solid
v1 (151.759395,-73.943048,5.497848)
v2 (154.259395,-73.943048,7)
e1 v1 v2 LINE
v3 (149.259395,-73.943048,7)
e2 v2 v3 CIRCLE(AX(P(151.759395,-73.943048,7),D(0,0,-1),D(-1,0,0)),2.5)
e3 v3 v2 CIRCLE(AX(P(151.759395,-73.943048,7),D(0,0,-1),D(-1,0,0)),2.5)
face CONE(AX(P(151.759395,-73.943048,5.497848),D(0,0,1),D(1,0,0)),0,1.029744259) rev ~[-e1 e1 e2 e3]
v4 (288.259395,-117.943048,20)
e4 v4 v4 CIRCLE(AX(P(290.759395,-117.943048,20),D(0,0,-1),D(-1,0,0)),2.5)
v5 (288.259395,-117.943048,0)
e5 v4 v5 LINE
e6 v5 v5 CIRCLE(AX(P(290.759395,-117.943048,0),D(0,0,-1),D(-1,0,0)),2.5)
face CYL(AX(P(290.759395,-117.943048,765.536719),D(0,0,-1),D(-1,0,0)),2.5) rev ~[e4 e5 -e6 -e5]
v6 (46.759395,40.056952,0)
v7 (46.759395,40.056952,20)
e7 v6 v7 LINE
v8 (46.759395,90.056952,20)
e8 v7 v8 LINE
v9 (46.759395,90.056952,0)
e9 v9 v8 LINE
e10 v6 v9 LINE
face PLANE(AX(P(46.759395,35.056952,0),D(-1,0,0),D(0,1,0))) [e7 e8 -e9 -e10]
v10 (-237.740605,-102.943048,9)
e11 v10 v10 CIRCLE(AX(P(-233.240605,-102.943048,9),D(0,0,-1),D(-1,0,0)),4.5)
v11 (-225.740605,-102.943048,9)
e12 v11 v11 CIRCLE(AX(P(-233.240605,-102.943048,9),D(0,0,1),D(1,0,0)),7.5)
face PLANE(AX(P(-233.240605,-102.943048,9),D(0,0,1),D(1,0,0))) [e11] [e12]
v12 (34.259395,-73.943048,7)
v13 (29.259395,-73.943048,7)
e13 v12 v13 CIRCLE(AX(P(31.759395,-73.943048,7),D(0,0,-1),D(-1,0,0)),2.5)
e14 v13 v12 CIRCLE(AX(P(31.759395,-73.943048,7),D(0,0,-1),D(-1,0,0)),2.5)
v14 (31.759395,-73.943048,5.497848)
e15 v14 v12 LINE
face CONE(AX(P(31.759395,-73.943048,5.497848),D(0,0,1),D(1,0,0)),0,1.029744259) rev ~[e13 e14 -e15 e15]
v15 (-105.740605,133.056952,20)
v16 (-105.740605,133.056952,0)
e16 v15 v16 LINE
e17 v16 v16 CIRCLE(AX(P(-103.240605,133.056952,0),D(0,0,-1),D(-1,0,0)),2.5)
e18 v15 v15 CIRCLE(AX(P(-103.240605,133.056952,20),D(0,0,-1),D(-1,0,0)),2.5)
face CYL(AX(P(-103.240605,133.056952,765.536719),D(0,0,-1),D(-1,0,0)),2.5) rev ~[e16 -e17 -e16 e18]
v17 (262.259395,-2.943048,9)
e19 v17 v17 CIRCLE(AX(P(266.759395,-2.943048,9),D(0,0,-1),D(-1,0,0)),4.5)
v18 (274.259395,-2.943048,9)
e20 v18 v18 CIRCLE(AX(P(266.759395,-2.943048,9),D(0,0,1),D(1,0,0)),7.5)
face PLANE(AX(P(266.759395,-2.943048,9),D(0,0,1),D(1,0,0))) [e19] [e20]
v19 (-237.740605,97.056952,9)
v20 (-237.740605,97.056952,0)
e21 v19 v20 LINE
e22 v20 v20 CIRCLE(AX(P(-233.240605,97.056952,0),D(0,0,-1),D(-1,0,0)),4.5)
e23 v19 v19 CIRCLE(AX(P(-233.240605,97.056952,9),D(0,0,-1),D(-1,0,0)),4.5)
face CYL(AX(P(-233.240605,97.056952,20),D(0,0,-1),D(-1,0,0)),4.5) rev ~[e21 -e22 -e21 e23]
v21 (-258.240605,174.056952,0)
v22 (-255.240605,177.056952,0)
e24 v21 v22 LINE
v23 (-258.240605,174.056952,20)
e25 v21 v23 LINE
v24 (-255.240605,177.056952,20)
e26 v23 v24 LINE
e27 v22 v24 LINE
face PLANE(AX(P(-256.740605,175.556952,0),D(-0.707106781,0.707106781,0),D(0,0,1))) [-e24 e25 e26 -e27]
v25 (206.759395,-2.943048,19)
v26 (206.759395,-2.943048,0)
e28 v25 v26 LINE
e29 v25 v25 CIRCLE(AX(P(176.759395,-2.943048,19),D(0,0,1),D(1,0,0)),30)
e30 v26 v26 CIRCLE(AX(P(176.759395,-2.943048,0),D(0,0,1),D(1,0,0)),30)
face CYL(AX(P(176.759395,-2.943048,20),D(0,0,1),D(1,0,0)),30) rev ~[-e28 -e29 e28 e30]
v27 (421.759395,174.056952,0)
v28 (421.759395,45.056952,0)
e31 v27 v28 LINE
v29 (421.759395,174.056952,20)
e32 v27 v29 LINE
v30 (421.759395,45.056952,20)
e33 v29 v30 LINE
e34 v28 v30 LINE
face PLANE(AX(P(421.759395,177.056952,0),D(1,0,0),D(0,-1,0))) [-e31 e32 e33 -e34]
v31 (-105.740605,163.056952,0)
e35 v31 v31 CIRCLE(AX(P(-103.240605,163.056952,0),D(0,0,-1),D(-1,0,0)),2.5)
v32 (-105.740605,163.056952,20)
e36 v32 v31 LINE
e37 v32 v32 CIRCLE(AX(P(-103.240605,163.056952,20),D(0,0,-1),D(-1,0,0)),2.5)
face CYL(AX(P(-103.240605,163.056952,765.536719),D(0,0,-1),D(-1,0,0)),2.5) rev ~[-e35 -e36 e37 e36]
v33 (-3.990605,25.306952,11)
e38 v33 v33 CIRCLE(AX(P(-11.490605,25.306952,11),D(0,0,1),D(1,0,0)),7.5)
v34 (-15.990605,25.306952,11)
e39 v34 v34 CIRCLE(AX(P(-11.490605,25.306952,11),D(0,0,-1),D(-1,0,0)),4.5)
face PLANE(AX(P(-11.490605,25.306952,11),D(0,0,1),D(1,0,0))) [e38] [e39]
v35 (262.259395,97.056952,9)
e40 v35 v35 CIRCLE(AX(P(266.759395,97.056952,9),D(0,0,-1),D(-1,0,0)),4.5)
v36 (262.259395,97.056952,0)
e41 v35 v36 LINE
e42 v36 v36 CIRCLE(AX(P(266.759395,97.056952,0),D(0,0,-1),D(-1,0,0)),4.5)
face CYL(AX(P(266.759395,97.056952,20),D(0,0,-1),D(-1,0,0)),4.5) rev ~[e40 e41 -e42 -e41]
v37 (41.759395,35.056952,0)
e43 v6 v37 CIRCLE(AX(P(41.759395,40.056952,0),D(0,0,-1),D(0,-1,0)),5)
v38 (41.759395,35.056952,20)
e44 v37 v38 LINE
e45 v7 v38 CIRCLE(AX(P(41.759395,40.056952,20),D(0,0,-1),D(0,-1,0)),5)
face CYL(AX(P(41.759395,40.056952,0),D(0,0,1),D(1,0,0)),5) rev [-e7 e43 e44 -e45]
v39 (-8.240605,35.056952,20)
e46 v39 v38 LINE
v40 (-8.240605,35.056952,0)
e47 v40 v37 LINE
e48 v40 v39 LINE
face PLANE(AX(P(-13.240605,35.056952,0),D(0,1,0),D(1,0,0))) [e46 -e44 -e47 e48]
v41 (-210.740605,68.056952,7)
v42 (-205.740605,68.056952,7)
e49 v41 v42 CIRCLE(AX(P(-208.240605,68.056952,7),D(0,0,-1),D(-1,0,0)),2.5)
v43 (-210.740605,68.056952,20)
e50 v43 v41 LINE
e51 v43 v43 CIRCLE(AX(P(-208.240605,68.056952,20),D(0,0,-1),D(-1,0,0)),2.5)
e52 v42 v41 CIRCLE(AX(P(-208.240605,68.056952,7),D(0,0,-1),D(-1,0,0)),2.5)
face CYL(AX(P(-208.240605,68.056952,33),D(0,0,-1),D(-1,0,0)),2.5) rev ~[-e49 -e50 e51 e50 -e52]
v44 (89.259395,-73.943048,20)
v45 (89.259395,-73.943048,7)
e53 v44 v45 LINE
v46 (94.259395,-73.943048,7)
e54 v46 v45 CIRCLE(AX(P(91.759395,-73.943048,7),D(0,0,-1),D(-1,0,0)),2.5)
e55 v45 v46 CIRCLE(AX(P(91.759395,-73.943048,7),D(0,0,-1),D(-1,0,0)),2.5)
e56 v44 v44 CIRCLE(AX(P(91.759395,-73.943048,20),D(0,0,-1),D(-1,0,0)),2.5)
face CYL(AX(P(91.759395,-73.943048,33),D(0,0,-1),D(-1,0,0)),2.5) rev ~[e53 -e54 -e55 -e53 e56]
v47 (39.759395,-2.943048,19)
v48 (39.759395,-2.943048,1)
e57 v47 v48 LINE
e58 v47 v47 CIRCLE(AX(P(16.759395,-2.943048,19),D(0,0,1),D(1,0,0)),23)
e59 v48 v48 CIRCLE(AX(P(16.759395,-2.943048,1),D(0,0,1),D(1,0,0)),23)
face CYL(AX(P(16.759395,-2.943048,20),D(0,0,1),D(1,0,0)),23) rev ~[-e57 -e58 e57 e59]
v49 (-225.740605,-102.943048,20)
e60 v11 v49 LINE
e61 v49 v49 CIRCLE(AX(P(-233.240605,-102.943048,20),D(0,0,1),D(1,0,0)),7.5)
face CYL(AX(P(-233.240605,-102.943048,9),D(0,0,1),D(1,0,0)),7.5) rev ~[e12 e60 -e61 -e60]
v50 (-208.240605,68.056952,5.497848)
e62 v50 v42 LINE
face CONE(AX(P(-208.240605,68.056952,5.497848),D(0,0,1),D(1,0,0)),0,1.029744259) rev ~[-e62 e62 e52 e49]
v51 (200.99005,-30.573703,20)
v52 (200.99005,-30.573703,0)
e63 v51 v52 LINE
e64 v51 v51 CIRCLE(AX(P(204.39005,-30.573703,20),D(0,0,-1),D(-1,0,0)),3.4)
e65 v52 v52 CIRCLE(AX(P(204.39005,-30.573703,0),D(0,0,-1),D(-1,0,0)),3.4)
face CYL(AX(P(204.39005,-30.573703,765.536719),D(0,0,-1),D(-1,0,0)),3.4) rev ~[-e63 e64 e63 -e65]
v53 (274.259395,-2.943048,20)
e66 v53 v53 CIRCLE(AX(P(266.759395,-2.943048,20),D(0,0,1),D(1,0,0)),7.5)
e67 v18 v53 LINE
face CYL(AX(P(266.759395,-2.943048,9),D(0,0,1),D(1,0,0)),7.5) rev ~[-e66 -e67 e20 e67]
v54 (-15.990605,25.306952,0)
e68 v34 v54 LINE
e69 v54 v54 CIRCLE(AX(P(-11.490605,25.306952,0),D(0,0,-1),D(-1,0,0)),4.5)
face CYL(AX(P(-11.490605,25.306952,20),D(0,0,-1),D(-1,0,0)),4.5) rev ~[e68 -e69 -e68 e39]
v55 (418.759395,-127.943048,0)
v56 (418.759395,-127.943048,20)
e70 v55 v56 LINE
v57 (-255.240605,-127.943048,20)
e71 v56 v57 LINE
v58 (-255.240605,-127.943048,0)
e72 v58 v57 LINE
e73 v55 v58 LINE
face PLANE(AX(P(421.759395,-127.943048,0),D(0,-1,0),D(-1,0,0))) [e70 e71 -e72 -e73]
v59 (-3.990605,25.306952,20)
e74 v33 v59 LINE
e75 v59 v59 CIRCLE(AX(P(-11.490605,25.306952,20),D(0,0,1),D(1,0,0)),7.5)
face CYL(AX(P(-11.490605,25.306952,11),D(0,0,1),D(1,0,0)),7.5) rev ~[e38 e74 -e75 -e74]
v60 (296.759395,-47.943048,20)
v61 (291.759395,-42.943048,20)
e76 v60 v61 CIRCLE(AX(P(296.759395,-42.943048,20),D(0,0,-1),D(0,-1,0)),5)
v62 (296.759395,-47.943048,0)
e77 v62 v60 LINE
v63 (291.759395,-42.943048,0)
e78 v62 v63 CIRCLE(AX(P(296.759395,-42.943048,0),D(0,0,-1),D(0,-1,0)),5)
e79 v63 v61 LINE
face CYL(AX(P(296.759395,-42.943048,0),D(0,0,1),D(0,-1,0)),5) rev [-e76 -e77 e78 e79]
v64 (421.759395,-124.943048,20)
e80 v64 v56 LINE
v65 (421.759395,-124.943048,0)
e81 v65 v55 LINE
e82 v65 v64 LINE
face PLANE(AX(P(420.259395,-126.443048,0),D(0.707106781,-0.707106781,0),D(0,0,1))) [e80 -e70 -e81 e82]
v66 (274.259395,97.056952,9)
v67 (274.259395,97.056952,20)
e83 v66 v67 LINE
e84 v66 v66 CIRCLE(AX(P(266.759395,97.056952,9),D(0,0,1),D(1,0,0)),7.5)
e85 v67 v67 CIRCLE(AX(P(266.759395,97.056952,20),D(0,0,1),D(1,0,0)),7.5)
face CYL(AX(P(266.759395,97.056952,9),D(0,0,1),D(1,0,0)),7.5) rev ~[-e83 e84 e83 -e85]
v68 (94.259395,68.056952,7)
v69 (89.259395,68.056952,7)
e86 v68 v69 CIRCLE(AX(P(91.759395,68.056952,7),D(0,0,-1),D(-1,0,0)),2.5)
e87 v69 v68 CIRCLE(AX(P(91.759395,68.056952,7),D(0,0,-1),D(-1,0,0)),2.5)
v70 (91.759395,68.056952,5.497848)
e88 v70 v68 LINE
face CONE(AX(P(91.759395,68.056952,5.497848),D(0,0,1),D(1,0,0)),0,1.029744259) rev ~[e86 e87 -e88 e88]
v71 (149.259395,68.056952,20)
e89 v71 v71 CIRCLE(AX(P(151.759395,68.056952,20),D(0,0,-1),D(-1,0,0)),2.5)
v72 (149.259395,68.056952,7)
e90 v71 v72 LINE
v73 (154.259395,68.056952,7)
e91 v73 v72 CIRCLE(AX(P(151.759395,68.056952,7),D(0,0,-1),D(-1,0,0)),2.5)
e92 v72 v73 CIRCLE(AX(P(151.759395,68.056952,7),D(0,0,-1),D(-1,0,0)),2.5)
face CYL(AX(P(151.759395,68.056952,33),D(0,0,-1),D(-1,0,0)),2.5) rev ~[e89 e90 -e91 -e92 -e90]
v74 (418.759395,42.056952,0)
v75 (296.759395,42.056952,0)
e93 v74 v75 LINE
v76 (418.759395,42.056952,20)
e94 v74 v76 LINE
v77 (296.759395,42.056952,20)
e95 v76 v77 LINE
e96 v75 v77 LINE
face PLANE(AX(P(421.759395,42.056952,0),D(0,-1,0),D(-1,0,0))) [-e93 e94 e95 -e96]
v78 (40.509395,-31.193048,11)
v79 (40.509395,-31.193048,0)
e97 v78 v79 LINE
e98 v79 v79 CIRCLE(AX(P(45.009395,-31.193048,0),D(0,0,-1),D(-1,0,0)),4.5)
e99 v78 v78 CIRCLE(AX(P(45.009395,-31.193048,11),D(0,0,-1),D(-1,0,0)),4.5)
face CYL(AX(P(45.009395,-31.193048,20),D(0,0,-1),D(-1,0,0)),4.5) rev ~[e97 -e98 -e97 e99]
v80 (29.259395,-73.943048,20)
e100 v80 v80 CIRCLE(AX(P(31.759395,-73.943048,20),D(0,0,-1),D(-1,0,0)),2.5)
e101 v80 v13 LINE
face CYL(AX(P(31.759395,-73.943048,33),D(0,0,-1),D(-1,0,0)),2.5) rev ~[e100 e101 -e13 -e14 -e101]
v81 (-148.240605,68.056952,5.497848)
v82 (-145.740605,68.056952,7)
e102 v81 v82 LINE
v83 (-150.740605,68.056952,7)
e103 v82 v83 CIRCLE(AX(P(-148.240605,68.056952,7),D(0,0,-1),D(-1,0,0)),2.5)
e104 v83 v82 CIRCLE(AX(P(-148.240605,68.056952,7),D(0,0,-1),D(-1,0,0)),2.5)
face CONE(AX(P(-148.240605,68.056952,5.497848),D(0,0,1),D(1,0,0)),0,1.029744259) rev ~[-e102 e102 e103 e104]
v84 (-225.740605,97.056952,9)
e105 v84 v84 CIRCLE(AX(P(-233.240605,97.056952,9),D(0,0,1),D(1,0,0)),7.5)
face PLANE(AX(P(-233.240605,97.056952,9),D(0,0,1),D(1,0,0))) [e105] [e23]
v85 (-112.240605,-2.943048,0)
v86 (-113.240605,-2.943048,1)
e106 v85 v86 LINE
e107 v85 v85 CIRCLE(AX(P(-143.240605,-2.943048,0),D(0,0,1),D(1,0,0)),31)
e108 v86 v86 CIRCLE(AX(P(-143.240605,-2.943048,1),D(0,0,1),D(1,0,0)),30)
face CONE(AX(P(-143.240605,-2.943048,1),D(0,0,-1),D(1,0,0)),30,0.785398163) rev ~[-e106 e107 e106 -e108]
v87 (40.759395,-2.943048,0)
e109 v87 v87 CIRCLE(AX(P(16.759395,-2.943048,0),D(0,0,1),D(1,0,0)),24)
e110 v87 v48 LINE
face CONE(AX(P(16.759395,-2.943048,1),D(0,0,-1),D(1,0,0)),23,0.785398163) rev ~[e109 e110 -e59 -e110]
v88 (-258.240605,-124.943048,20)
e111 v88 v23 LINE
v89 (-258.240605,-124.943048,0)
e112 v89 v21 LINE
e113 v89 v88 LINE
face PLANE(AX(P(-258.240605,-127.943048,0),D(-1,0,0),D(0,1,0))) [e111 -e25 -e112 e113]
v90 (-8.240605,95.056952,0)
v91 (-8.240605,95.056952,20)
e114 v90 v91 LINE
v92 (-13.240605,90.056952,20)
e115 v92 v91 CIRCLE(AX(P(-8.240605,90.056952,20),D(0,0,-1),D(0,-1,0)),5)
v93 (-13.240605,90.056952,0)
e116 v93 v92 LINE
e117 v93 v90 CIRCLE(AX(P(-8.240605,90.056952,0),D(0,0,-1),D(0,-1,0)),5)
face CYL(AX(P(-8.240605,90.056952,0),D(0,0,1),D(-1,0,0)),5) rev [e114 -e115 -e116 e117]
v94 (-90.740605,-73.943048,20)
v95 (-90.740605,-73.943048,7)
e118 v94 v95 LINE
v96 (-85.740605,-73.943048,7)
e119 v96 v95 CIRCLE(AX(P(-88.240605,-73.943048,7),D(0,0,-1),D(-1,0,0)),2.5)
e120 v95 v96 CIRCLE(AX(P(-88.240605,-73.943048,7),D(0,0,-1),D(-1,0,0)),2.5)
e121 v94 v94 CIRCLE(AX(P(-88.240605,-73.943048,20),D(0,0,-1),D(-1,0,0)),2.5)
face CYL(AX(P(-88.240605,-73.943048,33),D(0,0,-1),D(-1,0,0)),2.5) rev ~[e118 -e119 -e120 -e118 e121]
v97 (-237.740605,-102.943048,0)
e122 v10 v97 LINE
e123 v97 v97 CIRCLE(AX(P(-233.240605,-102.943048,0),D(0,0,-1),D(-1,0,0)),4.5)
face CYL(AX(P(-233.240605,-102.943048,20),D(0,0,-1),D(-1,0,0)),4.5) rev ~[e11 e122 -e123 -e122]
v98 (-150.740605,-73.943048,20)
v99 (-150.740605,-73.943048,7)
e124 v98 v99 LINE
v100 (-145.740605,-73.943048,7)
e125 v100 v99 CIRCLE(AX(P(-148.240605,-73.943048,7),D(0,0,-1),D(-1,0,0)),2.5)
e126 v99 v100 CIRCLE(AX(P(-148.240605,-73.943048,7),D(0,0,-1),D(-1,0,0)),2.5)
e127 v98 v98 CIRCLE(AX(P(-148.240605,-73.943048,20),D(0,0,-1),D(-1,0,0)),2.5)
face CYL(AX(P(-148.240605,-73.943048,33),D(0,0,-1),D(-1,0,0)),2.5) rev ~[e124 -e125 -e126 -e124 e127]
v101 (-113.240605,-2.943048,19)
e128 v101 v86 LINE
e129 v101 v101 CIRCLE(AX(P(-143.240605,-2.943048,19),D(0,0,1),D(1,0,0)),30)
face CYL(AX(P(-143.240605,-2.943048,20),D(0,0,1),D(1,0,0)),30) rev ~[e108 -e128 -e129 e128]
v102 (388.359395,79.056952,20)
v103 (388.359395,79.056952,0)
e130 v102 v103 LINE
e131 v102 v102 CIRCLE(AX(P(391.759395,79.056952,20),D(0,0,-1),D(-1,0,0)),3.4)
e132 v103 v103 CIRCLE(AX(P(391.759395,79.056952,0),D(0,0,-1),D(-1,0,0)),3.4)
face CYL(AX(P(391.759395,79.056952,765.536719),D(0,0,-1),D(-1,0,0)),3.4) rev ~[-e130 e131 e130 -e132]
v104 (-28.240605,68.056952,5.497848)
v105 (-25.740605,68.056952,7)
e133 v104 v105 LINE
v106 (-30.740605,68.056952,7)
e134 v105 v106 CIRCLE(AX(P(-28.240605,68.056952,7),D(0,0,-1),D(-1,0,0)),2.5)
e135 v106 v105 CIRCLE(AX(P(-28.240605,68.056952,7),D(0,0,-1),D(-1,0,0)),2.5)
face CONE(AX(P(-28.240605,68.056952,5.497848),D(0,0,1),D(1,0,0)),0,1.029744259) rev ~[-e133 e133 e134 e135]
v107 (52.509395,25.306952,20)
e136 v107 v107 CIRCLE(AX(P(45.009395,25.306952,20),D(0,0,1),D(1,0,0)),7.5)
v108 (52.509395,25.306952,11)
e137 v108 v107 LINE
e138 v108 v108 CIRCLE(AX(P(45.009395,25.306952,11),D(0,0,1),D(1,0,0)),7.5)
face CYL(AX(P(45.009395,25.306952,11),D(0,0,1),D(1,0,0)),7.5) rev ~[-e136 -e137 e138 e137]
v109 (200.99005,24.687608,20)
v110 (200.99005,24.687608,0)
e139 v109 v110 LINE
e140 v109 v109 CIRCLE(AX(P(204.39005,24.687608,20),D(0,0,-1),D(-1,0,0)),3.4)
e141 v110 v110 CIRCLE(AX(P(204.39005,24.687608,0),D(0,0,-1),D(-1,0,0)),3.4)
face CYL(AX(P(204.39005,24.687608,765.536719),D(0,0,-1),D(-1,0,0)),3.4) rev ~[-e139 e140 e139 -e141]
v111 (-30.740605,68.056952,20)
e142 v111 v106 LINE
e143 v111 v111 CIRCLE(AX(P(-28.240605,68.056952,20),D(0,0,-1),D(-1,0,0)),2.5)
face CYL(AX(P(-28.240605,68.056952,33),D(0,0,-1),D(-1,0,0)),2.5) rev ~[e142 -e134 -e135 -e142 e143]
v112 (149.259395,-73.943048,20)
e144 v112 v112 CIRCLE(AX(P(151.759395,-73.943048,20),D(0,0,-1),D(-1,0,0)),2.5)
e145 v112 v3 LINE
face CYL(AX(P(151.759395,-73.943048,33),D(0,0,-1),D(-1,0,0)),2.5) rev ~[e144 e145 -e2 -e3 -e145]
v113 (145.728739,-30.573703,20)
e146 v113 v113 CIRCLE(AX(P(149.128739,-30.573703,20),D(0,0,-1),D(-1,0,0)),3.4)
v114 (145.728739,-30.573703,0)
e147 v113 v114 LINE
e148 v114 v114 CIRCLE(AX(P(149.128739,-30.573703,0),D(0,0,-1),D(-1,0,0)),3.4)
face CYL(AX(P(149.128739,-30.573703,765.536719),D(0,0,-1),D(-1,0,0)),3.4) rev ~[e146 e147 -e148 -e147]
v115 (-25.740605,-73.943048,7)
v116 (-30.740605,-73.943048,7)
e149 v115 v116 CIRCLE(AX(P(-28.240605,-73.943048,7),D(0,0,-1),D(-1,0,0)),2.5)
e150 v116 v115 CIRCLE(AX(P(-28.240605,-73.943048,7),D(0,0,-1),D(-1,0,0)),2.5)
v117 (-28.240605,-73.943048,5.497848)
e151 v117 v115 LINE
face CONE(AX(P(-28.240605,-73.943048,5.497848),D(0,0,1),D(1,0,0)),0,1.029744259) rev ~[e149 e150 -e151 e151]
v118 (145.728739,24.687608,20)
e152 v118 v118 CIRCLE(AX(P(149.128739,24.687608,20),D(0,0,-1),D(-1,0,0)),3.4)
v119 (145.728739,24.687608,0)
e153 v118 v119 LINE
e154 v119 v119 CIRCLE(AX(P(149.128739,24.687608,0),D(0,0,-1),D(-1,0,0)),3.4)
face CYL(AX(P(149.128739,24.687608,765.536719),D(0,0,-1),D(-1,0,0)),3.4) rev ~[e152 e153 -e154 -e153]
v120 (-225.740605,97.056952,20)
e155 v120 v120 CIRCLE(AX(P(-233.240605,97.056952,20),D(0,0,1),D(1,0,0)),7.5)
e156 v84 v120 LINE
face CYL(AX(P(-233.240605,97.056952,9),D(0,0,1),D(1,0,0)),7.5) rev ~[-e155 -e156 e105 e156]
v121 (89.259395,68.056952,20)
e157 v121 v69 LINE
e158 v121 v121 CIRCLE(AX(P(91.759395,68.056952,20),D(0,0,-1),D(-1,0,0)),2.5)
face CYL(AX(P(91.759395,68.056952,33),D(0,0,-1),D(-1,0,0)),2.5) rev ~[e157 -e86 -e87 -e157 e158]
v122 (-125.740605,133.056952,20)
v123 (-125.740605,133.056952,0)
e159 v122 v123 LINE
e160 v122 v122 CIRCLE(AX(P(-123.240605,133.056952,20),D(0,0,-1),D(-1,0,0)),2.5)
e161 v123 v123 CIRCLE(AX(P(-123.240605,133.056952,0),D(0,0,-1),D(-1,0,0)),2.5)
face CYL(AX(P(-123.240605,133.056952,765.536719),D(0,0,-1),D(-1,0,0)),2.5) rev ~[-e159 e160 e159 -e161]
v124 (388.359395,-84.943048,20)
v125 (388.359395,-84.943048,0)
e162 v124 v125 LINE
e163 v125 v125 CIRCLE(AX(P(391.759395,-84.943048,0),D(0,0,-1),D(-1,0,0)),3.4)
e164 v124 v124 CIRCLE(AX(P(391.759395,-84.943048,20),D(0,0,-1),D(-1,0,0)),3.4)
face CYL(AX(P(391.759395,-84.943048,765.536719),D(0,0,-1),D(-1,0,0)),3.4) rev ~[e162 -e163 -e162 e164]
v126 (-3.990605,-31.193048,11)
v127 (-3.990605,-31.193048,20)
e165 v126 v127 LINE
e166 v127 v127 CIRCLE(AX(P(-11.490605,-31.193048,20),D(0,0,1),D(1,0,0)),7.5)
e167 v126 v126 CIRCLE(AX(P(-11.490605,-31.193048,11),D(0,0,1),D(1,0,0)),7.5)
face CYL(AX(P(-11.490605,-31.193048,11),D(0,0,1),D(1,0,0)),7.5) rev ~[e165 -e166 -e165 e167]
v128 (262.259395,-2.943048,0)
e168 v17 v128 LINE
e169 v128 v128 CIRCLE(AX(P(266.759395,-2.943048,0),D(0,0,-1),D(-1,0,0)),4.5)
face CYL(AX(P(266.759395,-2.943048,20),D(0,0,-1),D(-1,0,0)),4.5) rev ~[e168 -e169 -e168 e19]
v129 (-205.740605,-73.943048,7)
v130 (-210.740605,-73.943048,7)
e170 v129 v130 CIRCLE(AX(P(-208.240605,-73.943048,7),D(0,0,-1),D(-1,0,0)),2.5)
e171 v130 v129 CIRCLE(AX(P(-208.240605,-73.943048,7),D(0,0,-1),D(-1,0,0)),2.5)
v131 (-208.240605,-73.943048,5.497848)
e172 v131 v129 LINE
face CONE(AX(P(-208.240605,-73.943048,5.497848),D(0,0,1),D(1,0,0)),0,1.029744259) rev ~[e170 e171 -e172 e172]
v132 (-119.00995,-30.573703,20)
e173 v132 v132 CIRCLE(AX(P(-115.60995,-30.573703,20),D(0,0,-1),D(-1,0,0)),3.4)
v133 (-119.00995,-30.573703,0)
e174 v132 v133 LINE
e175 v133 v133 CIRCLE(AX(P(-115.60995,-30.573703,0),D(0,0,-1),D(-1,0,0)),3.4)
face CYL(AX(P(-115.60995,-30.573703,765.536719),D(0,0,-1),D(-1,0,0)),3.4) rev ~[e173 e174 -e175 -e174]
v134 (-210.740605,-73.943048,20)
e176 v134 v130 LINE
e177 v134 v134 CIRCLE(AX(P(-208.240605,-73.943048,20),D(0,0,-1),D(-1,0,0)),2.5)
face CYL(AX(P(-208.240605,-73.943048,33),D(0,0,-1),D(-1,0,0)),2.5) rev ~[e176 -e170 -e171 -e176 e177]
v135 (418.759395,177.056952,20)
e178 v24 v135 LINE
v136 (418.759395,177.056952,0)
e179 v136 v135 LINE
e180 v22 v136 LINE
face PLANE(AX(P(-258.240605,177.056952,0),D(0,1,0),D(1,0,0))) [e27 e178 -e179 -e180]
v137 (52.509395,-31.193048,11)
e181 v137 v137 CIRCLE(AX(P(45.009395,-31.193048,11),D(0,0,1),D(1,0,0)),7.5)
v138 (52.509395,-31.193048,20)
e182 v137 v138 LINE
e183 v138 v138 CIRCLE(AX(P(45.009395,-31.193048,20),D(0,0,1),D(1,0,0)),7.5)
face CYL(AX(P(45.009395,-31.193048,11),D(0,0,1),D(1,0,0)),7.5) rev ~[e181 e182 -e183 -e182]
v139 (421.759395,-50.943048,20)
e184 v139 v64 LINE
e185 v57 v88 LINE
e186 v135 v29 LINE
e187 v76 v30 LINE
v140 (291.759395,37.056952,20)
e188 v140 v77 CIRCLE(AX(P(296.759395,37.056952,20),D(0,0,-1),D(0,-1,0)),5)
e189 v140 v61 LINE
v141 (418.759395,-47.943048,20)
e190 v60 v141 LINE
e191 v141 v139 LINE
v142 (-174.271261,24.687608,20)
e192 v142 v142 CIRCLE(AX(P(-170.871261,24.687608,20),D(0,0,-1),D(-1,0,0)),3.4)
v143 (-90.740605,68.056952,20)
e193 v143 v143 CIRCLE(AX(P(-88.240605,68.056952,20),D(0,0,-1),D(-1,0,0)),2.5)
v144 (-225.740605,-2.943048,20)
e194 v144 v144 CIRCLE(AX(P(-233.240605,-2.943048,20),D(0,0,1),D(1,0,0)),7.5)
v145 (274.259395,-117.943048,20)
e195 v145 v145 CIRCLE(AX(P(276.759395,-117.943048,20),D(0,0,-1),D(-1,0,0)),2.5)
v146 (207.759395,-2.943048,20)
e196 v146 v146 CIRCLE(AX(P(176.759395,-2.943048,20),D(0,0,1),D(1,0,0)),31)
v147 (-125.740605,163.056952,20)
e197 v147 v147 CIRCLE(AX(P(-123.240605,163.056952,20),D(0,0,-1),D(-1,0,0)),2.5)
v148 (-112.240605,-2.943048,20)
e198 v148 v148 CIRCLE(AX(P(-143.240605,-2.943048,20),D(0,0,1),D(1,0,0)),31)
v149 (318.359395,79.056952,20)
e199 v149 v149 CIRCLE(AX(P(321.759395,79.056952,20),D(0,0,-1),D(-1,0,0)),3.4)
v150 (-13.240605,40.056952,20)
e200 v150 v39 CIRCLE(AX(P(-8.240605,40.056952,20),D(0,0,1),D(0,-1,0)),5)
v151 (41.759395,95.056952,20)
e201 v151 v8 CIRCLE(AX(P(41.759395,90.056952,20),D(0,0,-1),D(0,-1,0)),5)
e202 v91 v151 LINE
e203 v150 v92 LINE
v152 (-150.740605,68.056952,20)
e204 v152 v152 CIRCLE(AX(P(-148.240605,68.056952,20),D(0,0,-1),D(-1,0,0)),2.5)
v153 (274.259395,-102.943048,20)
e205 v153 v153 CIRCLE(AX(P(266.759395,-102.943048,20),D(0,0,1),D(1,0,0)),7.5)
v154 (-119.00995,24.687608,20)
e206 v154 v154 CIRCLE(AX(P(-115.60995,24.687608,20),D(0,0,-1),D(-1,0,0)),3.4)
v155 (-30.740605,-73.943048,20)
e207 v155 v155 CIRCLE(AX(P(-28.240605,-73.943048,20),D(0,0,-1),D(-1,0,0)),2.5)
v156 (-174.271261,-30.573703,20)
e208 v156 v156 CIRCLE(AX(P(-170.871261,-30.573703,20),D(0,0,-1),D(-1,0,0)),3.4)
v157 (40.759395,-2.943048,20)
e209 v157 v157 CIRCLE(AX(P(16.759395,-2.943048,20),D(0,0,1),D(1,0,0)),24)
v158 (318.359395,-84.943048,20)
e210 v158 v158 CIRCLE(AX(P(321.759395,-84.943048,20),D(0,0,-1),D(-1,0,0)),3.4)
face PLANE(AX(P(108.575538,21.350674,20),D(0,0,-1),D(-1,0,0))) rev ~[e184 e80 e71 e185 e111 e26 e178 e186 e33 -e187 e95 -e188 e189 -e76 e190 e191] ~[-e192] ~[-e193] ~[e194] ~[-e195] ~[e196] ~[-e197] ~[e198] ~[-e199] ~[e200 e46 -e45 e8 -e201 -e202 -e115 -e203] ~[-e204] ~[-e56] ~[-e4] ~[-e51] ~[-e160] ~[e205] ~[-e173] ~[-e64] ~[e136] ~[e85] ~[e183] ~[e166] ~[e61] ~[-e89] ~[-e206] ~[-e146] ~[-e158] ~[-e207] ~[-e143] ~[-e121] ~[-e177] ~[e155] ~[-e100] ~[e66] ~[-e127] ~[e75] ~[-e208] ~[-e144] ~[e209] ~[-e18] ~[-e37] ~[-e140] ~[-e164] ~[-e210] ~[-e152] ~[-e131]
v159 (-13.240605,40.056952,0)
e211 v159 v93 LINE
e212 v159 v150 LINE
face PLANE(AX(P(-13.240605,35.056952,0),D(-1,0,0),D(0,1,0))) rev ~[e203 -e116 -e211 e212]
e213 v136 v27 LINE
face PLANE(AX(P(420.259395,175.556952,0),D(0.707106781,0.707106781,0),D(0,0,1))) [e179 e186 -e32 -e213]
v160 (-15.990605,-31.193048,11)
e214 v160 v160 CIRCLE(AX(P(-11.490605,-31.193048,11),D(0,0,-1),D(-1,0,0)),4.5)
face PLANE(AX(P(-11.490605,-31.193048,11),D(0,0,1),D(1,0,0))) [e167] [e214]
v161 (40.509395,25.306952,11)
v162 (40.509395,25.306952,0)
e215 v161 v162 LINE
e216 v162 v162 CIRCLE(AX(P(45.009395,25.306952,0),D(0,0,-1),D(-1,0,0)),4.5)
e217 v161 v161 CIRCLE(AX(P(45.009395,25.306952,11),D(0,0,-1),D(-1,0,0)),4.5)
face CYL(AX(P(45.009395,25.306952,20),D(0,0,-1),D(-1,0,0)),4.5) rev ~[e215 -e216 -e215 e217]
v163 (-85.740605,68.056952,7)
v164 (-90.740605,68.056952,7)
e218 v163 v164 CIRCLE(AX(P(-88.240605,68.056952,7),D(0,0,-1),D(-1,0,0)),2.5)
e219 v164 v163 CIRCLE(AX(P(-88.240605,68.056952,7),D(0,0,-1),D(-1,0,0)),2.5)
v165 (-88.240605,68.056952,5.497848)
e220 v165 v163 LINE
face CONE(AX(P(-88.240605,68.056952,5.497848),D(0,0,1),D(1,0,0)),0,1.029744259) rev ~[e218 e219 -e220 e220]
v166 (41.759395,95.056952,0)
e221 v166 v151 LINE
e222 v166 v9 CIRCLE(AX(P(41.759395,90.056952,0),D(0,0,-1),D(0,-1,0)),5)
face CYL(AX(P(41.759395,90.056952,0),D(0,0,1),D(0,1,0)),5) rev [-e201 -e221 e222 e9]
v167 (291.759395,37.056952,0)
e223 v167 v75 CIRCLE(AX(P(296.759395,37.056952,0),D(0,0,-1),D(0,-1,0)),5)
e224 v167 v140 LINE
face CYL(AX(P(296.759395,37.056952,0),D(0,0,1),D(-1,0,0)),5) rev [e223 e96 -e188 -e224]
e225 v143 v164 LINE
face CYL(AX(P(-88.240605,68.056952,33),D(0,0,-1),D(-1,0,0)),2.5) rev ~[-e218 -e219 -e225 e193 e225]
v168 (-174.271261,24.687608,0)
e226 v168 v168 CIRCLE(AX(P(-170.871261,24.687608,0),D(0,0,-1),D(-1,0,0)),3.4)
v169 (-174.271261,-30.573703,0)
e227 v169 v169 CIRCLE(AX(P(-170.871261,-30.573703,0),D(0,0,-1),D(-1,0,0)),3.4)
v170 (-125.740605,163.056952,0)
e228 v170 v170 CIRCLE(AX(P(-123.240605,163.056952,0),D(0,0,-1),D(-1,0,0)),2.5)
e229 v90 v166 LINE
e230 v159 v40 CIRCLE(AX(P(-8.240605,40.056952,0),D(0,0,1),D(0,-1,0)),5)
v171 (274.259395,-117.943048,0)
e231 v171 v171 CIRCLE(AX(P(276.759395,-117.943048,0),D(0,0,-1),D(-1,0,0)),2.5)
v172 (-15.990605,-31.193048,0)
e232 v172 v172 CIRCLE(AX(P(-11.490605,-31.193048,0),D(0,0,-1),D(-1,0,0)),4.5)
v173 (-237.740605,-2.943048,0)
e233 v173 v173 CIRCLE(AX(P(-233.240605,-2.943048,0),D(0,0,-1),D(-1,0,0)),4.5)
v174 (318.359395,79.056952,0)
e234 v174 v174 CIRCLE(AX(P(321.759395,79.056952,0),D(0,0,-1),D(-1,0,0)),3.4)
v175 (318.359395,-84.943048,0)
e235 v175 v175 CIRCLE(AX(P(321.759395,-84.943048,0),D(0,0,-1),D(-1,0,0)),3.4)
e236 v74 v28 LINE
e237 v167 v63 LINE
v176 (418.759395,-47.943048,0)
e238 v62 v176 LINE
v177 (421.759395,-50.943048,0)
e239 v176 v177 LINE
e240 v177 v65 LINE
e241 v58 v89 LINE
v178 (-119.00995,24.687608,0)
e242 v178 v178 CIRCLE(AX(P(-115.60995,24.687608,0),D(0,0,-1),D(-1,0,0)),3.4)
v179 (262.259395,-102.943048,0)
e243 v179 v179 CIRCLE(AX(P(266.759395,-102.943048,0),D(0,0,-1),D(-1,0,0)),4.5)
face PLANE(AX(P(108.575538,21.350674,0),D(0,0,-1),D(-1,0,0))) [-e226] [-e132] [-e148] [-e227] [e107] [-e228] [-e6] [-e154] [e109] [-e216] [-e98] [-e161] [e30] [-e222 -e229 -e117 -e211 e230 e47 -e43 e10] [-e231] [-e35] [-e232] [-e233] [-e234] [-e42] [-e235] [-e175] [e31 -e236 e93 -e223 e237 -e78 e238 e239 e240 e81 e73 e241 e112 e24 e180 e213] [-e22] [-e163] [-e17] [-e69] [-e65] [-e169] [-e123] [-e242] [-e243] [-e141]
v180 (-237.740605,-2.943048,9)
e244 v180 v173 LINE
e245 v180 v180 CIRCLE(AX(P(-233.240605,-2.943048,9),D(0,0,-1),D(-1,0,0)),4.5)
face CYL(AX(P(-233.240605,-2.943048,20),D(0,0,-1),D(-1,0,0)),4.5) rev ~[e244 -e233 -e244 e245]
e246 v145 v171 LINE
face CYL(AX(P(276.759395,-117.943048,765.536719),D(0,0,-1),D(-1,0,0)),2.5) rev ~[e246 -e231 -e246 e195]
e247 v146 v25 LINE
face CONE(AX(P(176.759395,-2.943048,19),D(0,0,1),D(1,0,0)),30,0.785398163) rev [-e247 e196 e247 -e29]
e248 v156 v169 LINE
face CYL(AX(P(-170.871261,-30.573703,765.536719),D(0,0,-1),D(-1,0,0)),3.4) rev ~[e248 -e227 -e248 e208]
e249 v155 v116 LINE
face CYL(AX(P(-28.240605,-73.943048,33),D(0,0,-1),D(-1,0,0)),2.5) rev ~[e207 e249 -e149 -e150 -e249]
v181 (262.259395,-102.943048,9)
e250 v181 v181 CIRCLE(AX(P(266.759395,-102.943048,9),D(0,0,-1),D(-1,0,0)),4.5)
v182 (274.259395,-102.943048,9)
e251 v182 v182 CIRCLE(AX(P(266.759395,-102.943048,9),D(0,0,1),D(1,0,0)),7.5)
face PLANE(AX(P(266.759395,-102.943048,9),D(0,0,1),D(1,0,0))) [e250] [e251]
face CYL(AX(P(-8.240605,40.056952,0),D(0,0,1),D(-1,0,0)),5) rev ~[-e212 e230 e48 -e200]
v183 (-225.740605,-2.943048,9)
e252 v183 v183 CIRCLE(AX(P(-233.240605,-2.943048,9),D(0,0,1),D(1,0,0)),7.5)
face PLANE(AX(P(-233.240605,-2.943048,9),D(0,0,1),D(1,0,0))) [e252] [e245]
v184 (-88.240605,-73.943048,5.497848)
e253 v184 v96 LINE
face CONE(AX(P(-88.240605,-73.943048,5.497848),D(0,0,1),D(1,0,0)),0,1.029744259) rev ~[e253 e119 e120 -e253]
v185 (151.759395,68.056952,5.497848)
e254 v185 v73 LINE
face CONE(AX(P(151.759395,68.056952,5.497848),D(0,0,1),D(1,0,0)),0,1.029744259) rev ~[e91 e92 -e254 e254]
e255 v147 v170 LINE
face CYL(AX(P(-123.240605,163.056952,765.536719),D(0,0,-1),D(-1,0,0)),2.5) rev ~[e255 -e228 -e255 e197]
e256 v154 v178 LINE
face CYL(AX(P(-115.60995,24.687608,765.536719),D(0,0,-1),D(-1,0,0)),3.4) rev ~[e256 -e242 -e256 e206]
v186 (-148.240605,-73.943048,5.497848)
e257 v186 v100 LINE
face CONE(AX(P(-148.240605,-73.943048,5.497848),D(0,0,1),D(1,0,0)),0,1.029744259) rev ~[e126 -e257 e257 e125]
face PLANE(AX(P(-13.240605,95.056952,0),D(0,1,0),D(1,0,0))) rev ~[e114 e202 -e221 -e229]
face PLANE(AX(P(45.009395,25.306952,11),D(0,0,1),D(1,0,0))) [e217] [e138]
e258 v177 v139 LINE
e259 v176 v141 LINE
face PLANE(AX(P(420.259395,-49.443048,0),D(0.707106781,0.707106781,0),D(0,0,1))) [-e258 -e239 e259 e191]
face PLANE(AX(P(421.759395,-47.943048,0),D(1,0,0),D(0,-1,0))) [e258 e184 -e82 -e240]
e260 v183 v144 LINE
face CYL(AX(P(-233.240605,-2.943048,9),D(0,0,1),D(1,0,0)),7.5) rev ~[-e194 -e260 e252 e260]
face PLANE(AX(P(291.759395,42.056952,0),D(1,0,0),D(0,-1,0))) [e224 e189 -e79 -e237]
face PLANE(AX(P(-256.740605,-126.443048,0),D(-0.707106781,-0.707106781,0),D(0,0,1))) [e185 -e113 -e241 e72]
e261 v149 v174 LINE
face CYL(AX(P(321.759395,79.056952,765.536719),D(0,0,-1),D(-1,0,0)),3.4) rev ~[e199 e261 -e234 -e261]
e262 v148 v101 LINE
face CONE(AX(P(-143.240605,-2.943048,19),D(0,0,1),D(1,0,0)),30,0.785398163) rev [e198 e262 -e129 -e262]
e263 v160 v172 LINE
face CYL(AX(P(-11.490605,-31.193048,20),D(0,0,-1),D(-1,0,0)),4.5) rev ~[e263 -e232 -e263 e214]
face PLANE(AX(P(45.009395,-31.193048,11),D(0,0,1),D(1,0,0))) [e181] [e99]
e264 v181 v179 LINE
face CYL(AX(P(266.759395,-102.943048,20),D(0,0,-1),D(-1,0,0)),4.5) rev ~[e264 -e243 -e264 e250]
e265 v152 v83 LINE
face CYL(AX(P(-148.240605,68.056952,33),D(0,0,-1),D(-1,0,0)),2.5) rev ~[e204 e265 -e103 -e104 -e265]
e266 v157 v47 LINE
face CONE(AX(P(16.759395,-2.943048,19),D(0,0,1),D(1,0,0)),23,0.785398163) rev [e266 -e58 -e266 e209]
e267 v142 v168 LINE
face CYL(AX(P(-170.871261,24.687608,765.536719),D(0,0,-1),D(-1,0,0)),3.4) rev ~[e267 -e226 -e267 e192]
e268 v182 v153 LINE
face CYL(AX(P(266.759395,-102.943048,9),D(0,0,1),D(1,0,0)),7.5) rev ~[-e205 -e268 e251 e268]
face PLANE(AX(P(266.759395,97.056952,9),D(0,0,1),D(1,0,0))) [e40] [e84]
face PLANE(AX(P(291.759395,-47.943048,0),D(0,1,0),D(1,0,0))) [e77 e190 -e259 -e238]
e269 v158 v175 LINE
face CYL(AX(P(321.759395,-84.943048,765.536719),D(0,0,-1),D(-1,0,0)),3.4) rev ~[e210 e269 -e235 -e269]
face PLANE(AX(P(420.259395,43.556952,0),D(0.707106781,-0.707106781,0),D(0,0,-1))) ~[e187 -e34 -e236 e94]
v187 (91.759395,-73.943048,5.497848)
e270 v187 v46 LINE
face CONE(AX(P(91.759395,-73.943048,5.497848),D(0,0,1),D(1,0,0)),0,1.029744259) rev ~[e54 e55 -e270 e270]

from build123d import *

# Parameters (mm, degrees)
SKETCH1_W             = 60
SKETCH1_H             = 60
BOSS_EXTRUDE1_DEPTH   = 20
FILLET1_R             = 5
CHAMFER1_SIZE         = 3
SKETCH2_R             = 30
SKETCH2_R_2           = 23
CUT_EXTRUDE1_DEPTH    = 20
CHAMFER2_SIZE         = 1
M8_TAPPED_HOLE1_D     = 6.8
M6_TAPPED_HOLE1_D     = 5
M6_TAPPED_HOLE2_D     = 5
M6_TAPPED_HOLE2_DEPTH = 13
M6_TAPPED_HOLE2_TIP   = 1.502151548
M8_TAPPED_HOLE2_D     = 6.8
M6_TAPPED_HOLE3_D     = 5
HOLE1_D               = 9
HOLE1_CBORE_D         = 15
HOLE1_CBORE_DEPTH     = 11
HOLE2_D               = 9
HOLE2_CBORE_D         = 15
HOLE2_CBORE_DEPTH     = 9


with BuildPart() as part:
    # Sketch1 → Boss-Extrude1 (new body)
    with BuildSketch(Plane.XY):
        Polygon((421.759394592, -47.943047911), (421.759394592, -127.943047911), (-258.240605408, -127.943047911), (-258.240605408, 177.056952089), (421.759394592, 177.056952089), (421.759394592, 42.056952089), (291.759394592, 42.056952089), (291.759394592, -47.943047911), align=None)
        with Locations((16.759394592, 65.056952089)):
            Rectangle(SKETCH1_W, SKETCH1_H, mode=Mode.SUBTRACT)
    extrude(amount=BOSS_EXTRUDE1_DEPTH)

    # Fillet1
    fillet1_edges = [part.edges().sort_by_distance(p)[0] for p in [
        (291.759394592, 42.056952089, 10),
        (291.759394592, -47.943047911, 10),
        (-13.240605408, 95.056952089, 10),
        (-13.240605408, 35.056952089, 10),
        (46.759394592, 35.056952089, 10),
        (46.759394592, 95.056952089, 10),
    ]]
    fillet(fillet1_edges, radius=FILLET1_R)

    # Chamfer1
    chamfer1_edges = [part.edges().sort_by_distance(p)[0] for p in [
        (-258.240605408, 177.056952089, 10),
        (421.759394592, 177.056952089, 10),
        (421.759394592, 42.056952089, 10),
        (421.759394592, -47.943047911, 10),
        (421.759394592, -127.943047911, 10),
        (-258.240605408, -127.943047911, 10),
    ]]
    chamfer(chamfer1_edges, length=CHAMFER1_SIZE)

    # Sketch2 → Cut-Extrude1 (cut)
    with BuildSketch(Plane.XY.offset(20)):
        with Locations((-143.240605408, -2.943047911)):
            Circle(SKETCH2_R)
        with Locations((16.759394592, -2.943047911)):
            Circle(SKETCH2_R_2)
        with Locations((176.759394592, -2.943047911)):
            Circle(SKETCH2_R)
    extrude(amount=-CUT_EXTRUDE1_DEPTH, mode=Mode.SUBTRACT)

    # Chamfer2
    chamfer2_edges = [part.edges().sort_by_distance(p)[0] for p in [
        (-173.240605408, -2.943047911, 0),
        (-173.240605408, -2.943047911, 20),
        (-6.240605408, -2.943047911, 0),
        (-6.240605408, -2.943047911, 20),
        (146.759394592, -2.943047911, 20),
    ]]
    chamfer(chamfer2_edges, length=CHAMFER2_SIZE)

    # M8 Tapped Hole1 (through all)
    with Locations(Plane.XY.offset(20)):
        with Locations((321.759394592, 79.056952089), (391.759394592, 79.056952089), (391.759394592, -84.943047911), (321.759394592, -84.943047911)):
            Hole(M8_TAPPED_HOLE1_D / 2)

    # M6 Tapped Hole1 (through all)
    with Locations(Plane.XY.offset(20)):
        with Locations((276.759394592, -117.943047911), (290.759394592, -117.943047911)):
            Hole(M6_TAPPED_HOLE1_D / 2)

    # M6 Tapped Hole2
    with Locations(Plane.XY.offset(20)):
        with Locations((-208.240605408, 68.056952089), (-208.240605408, -73.943047911), (-148.240605408, -73.943047911), (-88.240605408, -73.943047911), (-88.240605408, 68.056952089), (-148.240605408, 68.056952089), (-28.240605408, 68.056952089), (-28.240605408, -73.943047911), (31.759394592, -73.943047911), (91.759394592, -73.943047911), (151.759394592, -73.943047911), (151.759394592, 68.056952089), (91.759394592, 68.056952089)):
            Hole(M6_TAPPED_HOLE2_D / 2, depth=M6_TAPPED_HOLE2_DEPTH)
            with Locations((0, 0, -(M6_TAPPED_HOLE2_DEPTH + M6_TAPPED_HOLE2_TIP / 2))):  # 118° drill point
                Cone(0, M6_TAPPED_HOLE2_D / 2, M6_TAPPED_HOLE2_TIP, mode=Mode.SUBTRACT)

    # M8 Tapped Hole2 (through all)
    with Locations(Plane.XY.offset(20)):
        with Locations((-170.871260926, 24.687607606), (-170.871260926, -30.573703429), (-115.609949891, -30.573703429), (-115.609949891, 24.687607606), (149.128739074, 24.687607606), (204.390050109, 24.687607606), (204.390050109, -30.573703429), (149.128739074, -30.573703429)):
            Hole(M8_TAPPED_HOLE2_D / 2)

    # M6 Tapped Hole3 (through all)
    with Locations(Plane.XY.offset(20)):
        with Locations((-123.240605408, 163.056952089), (-103.240605408, 163.056952089), (-103.240605408, 133.056952089), (-123.240605408, 133.056952089)):
            Hole(M6_TAPPED_HOLE3_D / 2)

    # Hole1 (through all)
    with Locations(Plane.XY.offset(20)):
        with Locations((-233.240605408, 97.056952089), (-233.240605408, -2.943047911), (-233.240605408, -102.943047911), (266.759394592, 97.056952089), (266.759394592, -102.943047911), (266.759394592, -2.943047911)):
            CounterBoreHole(HOLE1_D / 2, HOLE1_CBORE_D / 2, HOLE1_CBORE_DEPTH)

    # Hole2 (through all)
    with Locations(Plane.XY.offset(20)):
        with Locations((-11.490605408, 25.306952089), (45.009394592, 25.306952089), (45.009394592, -31.193047911), (-11.490605408, -31.193047911)):
            CounterBoreHole(HOLE2_D / 2, HOLE2_CBORE_D / 2, HOLE2_CBORE_DEPTH)


solid = part.part
